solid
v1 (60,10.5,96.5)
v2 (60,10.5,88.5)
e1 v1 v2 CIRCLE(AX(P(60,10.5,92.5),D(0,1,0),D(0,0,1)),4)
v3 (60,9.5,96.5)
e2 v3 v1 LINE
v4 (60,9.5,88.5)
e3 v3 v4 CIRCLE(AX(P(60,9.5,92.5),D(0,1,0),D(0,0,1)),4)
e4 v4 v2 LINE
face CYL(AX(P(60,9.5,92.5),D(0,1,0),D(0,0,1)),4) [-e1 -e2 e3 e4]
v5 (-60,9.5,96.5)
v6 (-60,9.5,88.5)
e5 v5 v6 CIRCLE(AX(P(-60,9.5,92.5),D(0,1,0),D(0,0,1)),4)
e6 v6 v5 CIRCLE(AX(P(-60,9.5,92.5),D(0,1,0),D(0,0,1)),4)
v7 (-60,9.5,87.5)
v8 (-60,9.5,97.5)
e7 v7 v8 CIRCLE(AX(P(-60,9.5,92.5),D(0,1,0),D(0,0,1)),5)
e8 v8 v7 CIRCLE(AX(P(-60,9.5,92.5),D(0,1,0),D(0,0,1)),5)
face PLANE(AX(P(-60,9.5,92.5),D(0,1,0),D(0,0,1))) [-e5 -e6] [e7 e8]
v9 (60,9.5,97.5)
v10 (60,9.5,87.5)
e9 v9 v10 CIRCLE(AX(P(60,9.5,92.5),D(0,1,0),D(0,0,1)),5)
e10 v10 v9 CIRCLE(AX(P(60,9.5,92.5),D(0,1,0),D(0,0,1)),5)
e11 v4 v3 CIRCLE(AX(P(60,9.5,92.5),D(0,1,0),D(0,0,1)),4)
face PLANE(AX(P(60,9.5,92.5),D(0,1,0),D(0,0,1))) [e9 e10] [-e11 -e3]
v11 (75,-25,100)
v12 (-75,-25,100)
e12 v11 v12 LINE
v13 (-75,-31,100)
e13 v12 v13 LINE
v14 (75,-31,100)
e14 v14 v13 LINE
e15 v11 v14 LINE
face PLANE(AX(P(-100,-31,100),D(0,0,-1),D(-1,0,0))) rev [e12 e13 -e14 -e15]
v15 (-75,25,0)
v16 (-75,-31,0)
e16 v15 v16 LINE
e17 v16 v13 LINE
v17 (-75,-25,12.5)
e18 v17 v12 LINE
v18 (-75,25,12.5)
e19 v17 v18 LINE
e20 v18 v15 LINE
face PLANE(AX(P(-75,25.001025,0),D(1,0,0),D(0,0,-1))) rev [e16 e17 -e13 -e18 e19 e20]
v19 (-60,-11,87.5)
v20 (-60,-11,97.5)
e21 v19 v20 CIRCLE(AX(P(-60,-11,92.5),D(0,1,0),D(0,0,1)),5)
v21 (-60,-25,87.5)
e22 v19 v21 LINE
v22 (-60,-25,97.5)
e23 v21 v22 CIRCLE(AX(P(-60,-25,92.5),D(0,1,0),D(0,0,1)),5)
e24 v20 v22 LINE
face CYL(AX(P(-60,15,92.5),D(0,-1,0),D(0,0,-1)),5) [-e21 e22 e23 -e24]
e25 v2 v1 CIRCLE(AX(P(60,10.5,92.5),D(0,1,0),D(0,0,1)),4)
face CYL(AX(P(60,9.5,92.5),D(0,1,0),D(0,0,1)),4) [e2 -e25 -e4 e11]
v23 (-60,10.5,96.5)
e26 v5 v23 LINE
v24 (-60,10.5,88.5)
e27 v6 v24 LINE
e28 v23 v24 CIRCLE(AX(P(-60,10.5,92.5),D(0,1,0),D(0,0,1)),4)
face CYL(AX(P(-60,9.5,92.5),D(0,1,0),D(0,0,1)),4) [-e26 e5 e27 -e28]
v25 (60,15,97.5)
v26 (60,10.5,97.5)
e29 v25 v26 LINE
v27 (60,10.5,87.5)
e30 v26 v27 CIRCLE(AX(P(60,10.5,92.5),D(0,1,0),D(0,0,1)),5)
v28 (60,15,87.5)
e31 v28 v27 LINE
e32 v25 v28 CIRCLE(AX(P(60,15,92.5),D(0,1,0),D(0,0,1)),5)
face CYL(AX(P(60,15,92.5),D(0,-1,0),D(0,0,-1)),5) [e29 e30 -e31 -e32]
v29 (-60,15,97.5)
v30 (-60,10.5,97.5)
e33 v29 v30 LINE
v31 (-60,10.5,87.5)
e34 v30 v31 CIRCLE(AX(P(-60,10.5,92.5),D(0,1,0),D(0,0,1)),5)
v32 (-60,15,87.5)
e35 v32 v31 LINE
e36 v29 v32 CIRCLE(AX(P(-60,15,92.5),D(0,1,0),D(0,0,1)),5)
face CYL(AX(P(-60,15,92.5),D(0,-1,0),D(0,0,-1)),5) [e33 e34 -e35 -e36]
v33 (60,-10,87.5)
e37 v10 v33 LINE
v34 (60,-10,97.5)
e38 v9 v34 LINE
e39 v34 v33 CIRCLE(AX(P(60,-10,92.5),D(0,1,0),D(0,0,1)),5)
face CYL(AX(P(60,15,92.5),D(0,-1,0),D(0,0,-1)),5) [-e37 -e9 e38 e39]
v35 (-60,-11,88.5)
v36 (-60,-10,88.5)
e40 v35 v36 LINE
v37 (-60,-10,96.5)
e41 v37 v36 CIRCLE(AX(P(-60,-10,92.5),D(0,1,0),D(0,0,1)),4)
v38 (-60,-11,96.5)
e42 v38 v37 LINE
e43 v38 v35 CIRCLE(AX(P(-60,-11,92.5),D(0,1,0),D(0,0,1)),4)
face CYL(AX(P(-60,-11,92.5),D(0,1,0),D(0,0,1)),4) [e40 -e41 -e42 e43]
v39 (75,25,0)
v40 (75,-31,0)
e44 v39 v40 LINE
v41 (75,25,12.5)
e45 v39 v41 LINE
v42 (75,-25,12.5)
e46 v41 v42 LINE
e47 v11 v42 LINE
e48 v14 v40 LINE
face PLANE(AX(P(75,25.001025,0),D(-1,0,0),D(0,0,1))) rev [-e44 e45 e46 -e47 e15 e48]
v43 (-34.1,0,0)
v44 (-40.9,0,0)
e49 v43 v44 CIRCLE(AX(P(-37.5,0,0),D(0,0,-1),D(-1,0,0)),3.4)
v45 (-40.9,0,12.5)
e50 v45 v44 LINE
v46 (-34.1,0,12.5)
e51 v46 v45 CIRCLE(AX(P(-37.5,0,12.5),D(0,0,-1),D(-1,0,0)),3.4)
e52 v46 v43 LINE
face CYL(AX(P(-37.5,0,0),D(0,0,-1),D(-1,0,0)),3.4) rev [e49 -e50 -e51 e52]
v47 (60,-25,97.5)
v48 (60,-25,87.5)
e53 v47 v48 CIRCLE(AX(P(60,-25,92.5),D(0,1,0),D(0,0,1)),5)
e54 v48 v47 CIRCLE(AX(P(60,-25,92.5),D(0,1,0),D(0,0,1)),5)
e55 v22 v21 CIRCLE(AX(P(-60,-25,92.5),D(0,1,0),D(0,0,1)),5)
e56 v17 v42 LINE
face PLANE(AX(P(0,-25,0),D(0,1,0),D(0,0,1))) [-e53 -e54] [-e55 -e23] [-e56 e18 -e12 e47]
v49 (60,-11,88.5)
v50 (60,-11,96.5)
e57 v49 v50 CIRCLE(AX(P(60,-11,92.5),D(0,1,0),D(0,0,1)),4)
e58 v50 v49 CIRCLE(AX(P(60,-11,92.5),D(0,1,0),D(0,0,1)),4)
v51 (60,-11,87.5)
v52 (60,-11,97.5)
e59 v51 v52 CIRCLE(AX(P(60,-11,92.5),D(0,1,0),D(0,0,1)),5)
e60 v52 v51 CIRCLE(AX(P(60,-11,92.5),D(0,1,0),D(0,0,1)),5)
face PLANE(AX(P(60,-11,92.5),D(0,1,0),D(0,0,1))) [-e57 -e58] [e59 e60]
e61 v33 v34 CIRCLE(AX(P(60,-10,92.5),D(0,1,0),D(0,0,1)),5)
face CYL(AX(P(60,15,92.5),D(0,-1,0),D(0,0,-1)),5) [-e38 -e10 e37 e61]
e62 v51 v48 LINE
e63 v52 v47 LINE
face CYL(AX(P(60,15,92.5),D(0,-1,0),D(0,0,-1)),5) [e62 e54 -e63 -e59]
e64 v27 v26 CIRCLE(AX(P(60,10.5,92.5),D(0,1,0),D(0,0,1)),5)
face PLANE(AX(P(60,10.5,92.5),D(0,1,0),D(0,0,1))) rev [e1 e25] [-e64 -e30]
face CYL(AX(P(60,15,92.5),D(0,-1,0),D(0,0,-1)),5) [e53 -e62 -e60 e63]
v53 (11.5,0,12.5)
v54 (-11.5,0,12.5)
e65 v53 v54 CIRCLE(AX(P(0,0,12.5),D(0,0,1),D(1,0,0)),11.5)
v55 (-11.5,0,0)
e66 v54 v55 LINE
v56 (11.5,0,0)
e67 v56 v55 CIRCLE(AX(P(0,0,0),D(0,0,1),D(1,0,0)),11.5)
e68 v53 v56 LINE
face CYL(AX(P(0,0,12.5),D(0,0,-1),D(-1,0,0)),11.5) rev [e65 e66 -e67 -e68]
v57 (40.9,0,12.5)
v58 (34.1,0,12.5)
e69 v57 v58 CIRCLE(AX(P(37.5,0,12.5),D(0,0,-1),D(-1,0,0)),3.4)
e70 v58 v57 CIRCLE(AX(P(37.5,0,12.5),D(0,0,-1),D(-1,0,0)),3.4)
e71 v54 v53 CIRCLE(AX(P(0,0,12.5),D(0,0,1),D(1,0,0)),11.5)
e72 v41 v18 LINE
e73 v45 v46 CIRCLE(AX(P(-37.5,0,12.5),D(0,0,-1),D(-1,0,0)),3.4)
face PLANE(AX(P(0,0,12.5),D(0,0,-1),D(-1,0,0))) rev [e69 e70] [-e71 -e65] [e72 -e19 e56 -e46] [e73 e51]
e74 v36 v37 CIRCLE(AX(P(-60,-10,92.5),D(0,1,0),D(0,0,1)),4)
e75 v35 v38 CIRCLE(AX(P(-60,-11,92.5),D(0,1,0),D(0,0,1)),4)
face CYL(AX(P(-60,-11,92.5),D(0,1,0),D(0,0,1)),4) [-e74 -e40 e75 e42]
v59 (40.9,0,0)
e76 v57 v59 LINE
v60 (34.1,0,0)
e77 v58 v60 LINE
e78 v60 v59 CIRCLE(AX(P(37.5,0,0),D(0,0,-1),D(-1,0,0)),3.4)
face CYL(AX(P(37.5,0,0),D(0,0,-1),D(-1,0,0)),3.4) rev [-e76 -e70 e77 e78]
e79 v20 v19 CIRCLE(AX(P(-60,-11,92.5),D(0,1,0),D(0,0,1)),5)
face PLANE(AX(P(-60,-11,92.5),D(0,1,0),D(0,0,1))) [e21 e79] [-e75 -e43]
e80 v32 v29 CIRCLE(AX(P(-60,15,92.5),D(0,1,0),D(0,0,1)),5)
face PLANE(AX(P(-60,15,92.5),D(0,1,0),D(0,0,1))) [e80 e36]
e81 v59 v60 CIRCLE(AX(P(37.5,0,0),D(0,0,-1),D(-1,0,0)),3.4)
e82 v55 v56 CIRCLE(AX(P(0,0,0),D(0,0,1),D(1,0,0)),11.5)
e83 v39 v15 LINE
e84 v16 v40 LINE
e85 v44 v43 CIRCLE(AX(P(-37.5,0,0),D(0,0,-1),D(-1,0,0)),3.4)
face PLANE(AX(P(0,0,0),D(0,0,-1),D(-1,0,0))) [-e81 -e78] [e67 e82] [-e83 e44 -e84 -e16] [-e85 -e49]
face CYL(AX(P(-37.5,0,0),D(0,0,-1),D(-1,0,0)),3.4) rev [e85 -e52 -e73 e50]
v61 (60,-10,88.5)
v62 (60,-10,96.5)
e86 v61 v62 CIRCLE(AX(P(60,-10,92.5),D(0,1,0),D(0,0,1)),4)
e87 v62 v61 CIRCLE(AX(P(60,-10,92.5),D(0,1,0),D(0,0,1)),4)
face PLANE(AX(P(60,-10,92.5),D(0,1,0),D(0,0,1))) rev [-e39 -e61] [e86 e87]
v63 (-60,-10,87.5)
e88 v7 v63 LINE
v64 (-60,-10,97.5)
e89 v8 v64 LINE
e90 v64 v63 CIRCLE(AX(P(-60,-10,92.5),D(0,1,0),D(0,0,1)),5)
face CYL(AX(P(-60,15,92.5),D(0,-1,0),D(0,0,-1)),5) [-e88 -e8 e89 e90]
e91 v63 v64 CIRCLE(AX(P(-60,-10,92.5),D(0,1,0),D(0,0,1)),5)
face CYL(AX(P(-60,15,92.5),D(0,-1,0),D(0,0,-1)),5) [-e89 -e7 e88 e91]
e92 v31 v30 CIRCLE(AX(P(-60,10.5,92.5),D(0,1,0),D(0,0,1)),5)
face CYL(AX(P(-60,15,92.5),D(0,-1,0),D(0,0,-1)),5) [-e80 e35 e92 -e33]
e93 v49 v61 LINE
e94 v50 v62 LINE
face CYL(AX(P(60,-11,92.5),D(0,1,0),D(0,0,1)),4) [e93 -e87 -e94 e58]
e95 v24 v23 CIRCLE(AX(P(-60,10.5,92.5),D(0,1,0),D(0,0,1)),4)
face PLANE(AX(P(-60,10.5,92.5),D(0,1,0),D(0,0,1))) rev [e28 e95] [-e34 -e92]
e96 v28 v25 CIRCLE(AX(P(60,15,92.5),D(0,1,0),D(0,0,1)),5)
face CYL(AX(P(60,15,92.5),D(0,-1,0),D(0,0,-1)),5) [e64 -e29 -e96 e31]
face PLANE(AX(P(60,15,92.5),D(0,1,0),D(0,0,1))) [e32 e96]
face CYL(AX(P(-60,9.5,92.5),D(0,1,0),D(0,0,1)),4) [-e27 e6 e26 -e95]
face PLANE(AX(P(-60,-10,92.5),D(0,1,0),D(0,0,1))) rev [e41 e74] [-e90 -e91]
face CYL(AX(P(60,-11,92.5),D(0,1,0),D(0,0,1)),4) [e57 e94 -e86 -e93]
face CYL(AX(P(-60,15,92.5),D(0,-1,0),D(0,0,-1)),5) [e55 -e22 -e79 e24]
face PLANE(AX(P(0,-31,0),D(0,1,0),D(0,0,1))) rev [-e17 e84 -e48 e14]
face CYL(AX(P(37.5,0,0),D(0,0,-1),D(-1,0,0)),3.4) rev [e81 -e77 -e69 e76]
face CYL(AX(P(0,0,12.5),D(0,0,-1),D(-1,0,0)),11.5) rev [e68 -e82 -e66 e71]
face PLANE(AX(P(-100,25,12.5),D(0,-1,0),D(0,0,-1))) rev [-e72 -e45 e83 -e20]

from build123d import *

# Parameters (mm, degrees)
SKETCH1_W                  = 200
SKETCH1_H                  = 50
SKETCH1_R                  = 11.5
BOSS_EXTRUDE1_DEPTH        = 12.5
SKETCH2_W                  = 200
SKETCH2_H                  = 100
BOSS_EXTRUDE2_DEPTH        = 6
M8X1_25_TAPPED_HOLE1_D     = 6.8
M8X1_25_TAPPED_HOLE1_DEPTH = 19.75
M8X1_25_TAPPED_HOLE1_TIP   = 2.042926105
SKETCH6_R                  = 5
BOSS_EXTRUDE3_DEPTH        = 40
SKETCH7_R                  = 7.408343544
SKETCH7_R_2                = 4
SKETCH7_R_3                = 9.473582921
CUT_EXTRUDE1_DEPTH         = 1
SKETCH8_R                  = 11.635219883
SKETCH8_R_2                = 4
SKETCH8_R_3                = 12.853619102
CUT_EXTRUDE2_DEPTH         = 1
CUT_EXTRUDE3_REACH         = 154.105
SKETCH9_W                  = 25
SKETCH9_H                  = 100


with BuildPart() as part:
    # Sketch1 → Boss-Extrude1 (new body)
    with BuildSketch(Plane.XY):
        Rectangle(SKETCH1_W, SKETCH1_H)
        Circle(SKETCH1_R, mode=Mode.SUBTRACT)
    extrude(amount=BOSS_EXTRUDE1_DEPTH)

    # Sketch2 → Boss-Extrude2 (add)
    with BuildSketch(Plane.XZ.offset(25)):
        with Locations((0, 50)):
            Rectangle(SKETCH2_W, SKETCH2_H)
    extrude(amount=BOSS_EXTRUDE2_DEPTH)

    # M8x1.25 Tapped Hole1
    with Locations(Plane(origin=(37.5, 0, 0), x_dir=(-1, 0, 0), z_dir=(0, 0, -1))):
        with Locations((0, 0), (75, 0)):
            Hole(M8X1_25_TAPPED_HOLE1_D / 2, depth=M8X1_25_TAPPED_HOLE1_DEPTH)
            with Locations((0, 0, -(M8X1_25_TAPPED_HOLE1_DEPTH + M8X1_25_TAPPED_HOLE1_TIP / 2))):  # 118° drill point
                Cone(0, M8X1_25_TAPPED_HOLE1_D / 2, M8X1_25_TAPPED_HOLE1_TIP, mode=Mode.SUBTRACT)

    # Sketch6 → Boss-Extrude3 (add)
    with BuildSketch(Plane(origin=(0, -25, 0), x_dir=(1, 0, 0), z_dir=(0, 1, 0))):
        with Locations(Location((60, -92.5, 0), (0, 0, 270))):
            Circle(SKETCH6_R)
        with Locations(Location((-60, -92.5, 0), (0, 0, 270))):
            Circle(SKETCH6_R)
    extrude(amount=BOSS_EXTRUDE3_DEPTH)

    # Sketch7 → Cut-Extrude1 (cut)
    # profile 1 of 2: a face of its own
    with BuildSketch(Plane(origin=(0, 10.5, 0), x_dir=(1, 0, 0), z_dir=(0, 1, 0))):
        with Locations((60, -92.5)):
            Circle(SKETCH7_R)
        with Locations(Location((60, -92.5, 0), (0, 0, 270))):
            Circle(SKETCH7_R_2, mode=Mode.SUBTRACT)
    # profile 2 of 2: a face of its own
    with BuildSketch(Plane(origin=(0, 10.5, 0), x_dir=(1, 0, 0), z_dir=(0, 1, 0))):
        with Locations((-60, -92.5)):
            Circle(SKETCH7_R_3)
        with Locations(Location((-60, -92.5, 0), (0, 0, 270))):
            Circle(SKETCH7_R_2, mode=Mode.SUBTRACT)
    extrude(amount=-CUT_EXTRUDE1_DEPTH, mode=Mode.SUBTRACT)

    # Sketch8 → Cut-Extrude2 (cut)
    # profile 1 of 2: a face of its own
    with BuildSketch(Plane(origin=(0, -10, 0), x_dir=(1, 0, 0), z_dir=(0, 1, 0))):
        with Locations((60, -92.5)):
            Circle(SKETCH8_R)
        with Locations(Location((60, -92.5, 0), (0, 0, 270))):
            Circle(SKETCH8_R_2, mode=Mode.SUBTRACT)
    # profile 2 of 2: a face of its own
    with BuildSketch(Plane(origin=(0, -10, 0), x_dir=(1, 0, 0), z_dir=(0, 1, 0))):
        with Locations((-60, -92.5)):
            Circle(SKETCH8_R_3)
        with Locations(Location((-60, -92.5, 0), (0, 0, 270))):
            Circle(SKETCH8_R_2, mode=Mode.SUBTRACT)
    extrude(amount=-CUT_EXTRUDE2_DEPTH, mode=Mode.SUBTRACT)

    # Sketch9 → Cut-Extrude3 (cut, up to next)
    with BuildSketch(Plane.XZ.offset(31), mode=Mode.PRIVATE) as cut_extrude3_sk1:
        with Locations((87.5, 50)):
            Rectangle(SKETCH9_W, SKETCH9_H)
    cut_extrude3_tool1 = extrude(cut_extrude3_sk1.sketch, amount=-CUT_EXTRUDE3_REACH, mode=Mode.PRIVATE) & part.part
    # Sketch9 → Cut-Extrude3 (cut, up to next)
    with BuildSketch(Plane.XZ.offset(31), mode=Mode.PRIVATE) as cut_extrude3_sk2:
        with Locations((-87.5, 50)):
            Rectangle(SKETCH9_W, SKETCH9_H)
    cut_extrude3_tool2 = extrude(cut_extrude3_sk2.sketch, amount=-CUT_EXTRUDE3_REACH, mode=Mode.PRIVATE) & part.part
    add(cut_extrude3_tool1.solids().sort_by_distance((87.5, -31, 50))[0], mode=Mode.SUBTRACT)
    add(cut_extrude3_tool2.solids().sort_by_distance((-87.5, -31, 50))[0], mode=Mode.SUBTRACT)


solid = part.part
